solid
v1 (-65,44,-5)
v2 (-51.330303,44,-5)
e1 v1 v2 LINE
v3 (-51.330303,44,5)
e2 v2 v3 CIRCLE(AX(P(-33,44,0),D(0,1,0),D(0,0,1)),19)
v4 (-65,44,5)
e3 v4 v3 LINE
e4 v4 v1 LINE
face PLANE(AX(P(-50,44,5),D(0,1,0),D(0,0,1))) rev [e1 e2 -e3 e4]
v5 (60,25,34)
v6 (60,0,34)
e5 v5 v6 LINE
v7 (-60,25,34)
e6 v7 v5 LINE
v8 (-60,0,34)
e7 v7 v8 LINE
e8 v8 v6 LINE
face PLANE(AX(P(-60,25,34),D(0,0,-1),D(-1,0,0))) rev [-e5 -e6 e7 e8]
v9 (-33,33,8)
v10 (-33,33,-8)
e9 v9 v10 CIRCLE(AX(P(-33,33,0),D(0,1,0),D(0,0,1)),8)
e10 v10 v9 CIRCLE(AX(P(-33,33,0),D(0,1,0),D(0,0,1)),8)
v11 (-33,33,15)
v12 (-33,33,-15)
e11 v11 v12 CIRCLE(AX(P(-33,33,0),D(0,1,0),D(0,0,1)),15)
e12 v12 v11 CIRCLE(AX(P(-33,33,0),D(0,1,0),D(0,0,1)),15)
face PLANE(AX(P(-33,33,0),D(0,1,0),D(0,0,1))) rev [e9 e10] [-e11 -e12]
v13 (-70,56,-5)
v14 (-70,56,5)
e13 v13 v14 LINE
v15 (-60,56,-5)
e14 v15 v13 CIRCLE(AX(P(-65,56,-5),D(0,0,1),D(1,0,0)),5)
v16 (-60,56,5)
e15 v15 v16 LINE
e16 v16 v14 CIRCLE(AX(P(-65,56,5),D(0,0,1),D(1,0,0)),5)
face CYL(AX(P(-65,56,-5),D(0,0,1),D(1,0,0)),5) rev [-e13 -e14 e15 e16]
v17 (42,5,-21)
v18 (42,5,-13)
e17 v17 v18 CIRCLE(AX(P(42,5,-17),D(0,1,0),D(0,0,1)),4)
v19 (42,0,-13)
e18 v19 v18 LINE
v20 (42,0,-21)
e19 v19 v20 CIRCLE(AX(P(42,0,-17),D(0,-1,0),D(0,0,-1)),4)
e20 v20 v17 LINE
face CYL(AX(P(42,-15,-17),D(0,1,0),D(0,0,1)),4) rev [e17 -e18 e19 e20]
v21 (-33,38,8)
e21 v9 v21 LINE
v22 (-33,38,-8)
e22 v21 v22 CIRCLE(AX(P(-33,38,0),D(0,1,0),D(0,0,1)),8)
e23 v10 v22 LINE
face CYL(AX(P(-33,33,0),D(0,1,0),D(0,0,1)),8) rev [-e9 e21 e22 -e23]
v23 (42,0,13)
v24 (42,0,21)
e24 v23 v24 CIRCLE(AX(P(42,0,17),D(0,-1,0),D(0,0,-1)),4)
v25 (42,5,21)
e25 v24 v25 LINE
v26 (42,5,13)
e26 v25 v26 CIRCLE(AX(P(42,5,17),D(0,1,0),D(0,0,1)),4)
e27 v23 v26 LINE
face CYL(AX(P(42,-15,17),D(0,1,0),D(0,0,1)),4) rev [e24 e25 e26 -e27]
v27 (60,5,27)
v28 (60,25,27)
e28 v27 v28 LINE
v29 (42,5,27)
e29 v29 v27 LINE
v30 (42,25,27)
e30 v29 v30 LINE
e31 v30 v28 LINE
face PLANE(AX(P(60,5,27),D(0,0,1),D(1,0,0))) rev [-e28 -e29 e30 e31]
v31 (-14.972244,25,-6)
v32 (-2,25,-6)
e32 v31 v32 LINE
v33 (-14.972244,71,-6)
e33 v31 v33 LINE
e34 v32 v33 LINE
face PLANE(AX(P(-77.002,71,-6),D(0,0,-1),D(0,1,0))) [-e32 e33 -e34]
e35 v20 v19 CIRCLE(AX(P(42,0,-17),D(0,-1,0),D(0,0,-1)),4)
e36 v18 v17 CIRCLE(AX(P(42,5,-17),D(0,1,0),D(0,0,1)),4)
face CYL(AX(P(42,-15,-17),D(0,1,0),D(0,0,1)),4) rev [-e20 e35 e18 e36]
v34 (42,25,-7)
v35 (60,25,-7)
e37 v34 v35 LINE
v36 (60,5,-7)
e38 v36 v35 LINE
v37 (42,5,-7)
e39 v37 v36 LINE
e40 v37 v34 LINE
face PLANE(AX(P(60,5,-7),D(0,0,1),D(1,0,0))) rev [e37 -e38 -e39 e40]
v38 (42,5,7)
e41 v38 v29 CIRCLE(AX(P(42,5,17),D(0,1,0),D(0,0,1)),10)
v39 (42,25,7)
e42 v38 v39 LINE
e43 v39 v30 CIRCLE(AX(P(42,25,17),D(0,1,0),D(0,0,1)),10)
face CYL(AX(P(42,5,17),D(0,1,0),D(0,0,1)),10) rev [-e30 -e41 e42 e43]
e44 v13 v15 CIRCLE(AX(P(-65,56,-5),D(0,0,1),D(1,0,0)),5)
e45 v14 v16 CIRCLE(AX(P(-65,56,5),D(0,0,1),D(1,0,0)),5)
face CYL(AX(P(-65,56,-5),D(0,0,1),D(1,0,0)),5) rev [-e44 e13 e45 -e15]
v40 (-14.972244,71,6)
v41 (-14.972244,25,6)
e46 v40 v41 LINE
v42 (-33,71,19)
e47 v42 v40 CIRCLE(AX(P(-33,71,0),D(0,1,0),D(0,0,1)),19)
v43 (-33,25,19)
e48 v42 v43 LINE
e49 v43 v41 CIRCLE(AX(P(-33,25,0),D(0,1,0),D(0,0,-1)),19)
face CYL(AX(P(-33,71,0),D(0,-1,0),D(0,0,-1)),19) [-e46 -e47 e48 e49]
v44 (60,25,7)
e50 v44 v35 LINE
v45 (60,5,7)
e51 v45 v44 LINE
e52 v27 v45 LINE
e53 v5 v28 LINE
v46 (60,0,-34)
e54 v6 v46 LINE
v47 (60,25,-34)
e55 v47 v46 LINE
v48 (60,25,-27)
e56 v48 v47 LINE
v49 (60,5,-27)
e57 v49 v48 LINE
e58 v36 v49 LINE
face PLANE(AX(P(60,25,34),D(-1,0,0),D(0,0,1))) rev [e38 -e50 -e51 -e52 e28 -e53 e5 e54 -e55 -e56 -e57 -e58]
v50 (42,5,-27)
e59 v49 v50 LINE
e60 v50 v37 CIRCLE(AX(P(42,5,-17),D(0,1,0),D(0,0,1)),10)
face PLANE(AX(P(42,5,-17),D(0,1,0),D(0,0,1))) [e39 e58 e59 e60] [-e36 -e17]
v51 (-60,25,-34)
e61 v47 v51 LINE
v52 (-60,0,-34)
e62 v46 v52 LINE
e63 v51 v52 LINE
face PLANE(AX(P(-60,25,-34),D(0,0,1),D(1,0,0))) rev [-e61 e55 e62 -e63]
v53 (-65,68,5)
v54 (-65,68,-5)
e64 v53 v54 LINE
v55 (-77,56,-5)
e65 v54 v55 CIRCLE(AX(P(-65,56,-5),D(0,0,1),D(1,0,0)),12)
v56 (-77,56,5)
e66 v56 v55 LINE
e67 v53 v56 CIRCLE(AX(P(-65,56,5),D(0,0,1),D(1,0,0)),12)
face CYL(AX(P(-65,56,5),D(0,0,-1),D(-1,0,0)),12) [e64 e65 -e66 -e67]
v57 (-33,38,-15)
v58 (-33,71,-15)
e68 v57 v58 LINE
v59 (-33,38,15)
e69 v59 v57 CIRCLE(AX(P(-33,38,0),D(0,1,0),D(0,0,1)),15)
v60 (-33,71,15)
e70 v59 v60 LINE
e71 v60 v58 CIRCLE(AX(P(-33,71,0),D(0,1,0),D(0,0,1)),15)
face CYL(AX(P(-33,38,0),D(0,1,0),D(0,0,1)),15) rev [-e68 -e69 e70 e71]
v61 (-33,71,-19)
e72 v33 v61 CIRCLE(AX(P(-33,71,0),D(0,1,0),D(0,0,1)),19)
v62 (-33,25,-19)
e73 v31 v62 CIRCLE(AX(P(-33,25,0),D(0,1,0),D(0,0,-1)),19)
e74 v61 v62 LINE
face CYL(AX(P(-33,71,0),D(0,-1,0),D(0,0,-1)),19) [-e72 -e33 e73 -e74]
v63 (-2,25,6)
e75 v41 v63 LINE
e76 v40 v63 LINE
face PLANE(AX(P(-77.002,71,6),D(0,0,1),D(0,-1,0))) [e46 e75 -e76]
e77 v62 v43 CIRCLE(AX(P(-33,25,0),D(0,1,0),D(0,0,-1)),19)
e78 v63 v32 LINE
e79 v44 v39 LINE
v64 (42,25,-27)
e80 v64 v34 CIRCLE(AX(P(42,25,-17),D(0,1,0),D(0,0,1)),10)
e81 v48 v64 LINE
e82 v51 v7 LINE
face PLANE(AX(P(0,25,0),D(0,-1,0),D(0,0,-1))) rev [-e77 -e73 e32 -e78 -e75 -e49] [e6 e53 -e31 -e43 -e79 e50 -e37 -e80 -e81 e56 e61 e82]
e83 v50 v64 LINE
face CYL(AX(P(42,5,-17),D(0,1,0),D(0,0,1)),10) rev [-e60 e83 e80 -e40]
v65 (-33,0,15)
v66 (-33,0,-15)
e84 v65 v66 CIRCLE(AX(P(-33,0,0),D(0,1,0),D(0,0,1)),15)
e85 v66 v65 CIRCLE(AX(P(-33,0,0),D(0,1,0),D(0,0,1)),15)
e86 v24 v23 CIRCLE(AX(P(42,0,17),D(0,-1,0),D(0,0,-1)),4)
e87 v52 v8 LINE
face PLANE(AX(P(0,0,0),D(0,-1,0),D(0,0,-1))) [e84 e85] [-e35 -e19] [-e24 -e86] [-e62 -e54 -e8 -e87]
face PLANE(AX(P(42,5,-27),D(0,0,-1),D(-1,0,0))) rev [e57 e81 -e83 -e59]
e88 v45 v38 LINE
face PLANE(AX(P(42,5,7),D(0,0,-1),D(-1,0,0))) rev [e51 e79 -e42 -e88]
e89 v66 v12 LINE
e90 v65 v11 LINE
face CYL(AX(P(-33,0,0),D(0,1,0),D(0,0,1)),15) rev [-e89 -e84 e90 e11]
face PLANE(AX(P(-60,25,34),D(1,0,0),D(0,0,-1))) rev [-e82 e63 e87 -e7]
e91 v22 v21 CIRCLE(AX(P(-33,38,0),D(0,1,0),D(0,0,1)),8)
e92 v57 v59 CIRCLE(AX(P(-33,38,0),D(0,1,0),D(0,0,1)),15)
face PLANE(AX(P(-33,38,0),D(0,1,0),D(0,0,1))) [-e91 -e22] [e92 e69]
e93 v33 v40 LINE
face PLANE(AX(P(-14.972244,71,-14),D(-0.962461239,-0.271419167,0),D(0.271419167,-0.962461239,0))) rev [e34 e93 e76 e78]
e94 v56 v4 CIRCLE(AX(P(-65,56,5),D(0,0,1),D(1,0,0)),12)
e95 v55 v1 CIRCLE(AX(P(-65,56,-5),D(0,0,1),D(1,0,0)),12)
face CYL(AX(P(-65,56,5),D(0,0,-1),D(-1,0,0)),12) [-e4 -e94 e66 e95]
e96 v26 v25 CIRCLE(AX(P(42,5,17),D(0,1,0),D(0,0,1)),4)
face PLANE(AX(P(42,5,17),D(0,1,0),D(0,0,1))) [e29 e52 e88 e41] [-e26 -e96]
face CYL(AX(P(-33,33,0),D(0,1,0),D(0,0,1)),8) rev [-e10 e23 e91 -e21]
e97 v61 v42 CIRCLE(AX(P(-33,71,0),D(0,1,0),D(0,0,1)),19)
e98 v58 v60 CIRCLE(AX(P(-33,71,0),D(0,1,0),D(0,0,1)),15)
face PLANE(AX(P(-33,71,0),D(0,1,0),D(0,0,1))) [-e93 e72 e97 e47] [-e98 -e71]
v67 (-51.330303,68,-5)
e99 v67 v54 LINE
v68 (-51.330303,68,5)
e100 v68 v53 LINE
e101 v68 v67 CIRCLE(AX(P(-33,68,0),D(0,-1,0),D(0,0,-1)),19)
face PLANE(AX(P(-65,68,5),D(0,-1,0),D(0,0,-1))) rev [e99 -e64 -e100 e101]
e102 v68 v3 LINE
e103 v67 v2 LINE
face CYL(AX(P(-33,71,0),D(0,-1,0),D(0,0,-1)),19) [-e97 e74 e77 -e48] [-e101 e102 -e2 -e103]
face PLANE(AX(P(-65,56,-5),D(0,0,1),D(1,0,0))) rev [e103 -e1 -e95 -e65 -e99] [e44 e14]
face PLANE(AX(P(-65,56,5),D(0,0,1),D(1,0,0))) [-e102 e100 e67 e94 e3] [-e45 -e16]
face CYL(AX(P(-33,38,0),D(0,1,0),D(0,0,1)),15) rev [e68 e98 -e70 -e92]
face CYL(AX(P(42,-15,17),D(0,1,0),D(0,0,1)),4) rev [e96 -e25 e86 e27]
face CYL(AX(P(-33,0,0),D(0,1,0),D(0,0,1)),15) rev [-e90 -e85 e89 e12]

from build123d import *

# Parameters (mm, degrees)
BASE_PLATE_SKETCH_W   = 120
BASE_PLATE_SKETCH_H   = 68
BASE_PLATE_DEPTH      = 25
PIVOT_BOSS_SKETCH_R   = 19
PIVOT_BOSS_38_DEPTH   = 46
UPPER_BORE_SKETCH_R   = 15
UPPER_BORE_30_DEPTH   = 33
BORE_STEP_SKETCH_R    = 8
BORE_STEP_16_DEPTH    = 5
LOWER_BORE_SKETCH_R   = 15
LOWER_BORE_30_DEPTH   = 33
SIDE_LUG_DEPTH        = 5
LUG_HOLE_SKETCH_R     = 5
LUG_HOLE_10_DEPTH     = 10
U_SLOTS_2X20_DEPTH    = 20
SLOT_RELIEF_SKETCH_R  = 4
SLOT_RELIEF_CUT_DEPTH = 20
GUSSET_RIB_REACH      = 110.729
GUSSET_RIB_END_RADIUS = 19
GUSSET_RIB_SKETCH_W   = 12
GUSSET_RIB_SKETCH_H   = 46
RIB_TRIM_CUT_DEPTH    = 20


with BuildPart() as part:
    # Base Plate Sketch → Base Plate (new body)
    with BuildSketch(Plane(origin=(0, 0, 0), x_dir=(1, 0, 0), z_dir=(0, 1, 0))):
        Rectangle(BASE_PLATE_SKETCH_W, BASE_PLATE_SKETCH_H)
    extrude(amount=BASE_PLATE_DEPTH)

    # Pivot Boss Sketch → Pivot Boss Ø38 (add)
    with BuildSketch(Plane(origin=(0, 25, 0), x_dir=(1, 0, 0), z_dir=(0, 1, 0))):
        with Locations(Location((-33, 0, 0), (0, 0, 90))):
            Circle(PIVOT_BOSS_SKETCH_R)
    extrude(amount=PIVOT_BOSS_38_DEPTH)

    # Upper Bore Sketch → Upper Bore Ø30 (cut)
    with BuildSketch(Plane(origin=(0, 71, 0), x_dir=(1, 0, 0), z_dir=(0, 1, 0))):
        with Locations(Location((-33, 0, 0), (0, 0, 270))):
            Circle(UPPER_BORE_SKETCH_R)
    extrude(amount=-UPPER_BORE_30_DEPTH, mode=Mode.SUBTRACT)

    # Bore Step Sketch → Bore Step Ø16 (cut)
    with BuildSketch(Plane(origin=(0, 38, 0), x_dir=(1, 0, 0), z_dir=(0, 1, 0))):
        with Locations(Location((-33, 0, 0), (0, 0, 270))):
            Circle(BORE_STEP_SKETCH_R)
    extrude(amount=-BORE_STEP_16_DEPTH, mode=Mode.SUBTRACT)

    # Lower Bore Sketch → Lower Bore Ø30 (cut)
    with BuildSketch(Plane(origin=(0, 33, 0), x_dir=(1, 0, 0), z_dir=(0, 1, 0))):
        with Locations(Location((-33, 0, 0), (0, 0, 270))):
            Circle(LOWER_BORE_SKETCH_R)
    extrude(amount=-LOWER_BORE_30_DEPTH, mode=Mode.SUBTRACT)

    # Side Lug Sketch → Side Lug (add, symmetric)
    with BuildSketch(Plane.XY):
        with BuildLine():
            Line((-65, 68), (-50, 68))
            Line((-50, 68), (-50, 44))
            Line((-50, 44), (-65, 44))
            ThreePointArc((-65, 44), (-77, 56), (-65, 68))
        make_face()
    extrude(amount=SIDE_LUG_DEPTH, both=True)

    # Lug Hole Sketch → Lug Hole Ø10 (cut)
    with BuildSketch(Plane.XY.offset(5)):
        with Locations((-65, 56)):
            Circle(LUG_HOLE_SKETCH_R)
    extrude(amount=-LUG_HOLE_10_DEPTH, mode=Mode.SUBTRACT)

    # U-Slots Sketch → U-Slots 2x20 (cut)
    with BuildSketch(Plane(origin=(0, 25, 0), x_dir=(1, 0, 0), z_dir=(0, 1, 0))):
        with BuildLine():
            Line((42, 27), (60, 27))
            Line((60, 27), (60, 7))
            Line((60, 7), (42, 7))
            ThreePointArc((42, 7), (32, 17), (42, 27))
        make_face()
        with BuildLine():
            Line((42, -7), (60, -7))
            Line((60, -7), (60, -27))
            Line((60, -27), (42, -27))
            ThreePointArc((42, -27), (32, -17), (42, -7))
        make_face()
    extrude(amount=-U_SLOTS_2X20_DEPTH, mode=Mode.SUBTRACT)

    # Slot Relief Sketch → Slot Relief Cut (cut)
    with BuildSketch(Plane(origin=(0, 5, 0), x_dir=(1, 0, 0), z_dir=(0, 1, 0))):
        with Locations(Location((42, 17, 0), (0, 0, 270))):
            Circle(SLOT_RELIEF_SKETCH_R)
        with Locations(Location((42, -17, 0), (0, 0, 270))):
            Circle(SLOT_RELIEF_SKETCH_R)
    extrude(amount=-SLOT_RELIEF_CUT_DEPTH, mode=Mode.SUBTRACT)

    # Gusset Rib: up to this cylinder (the profile starts outside it)
    gusset_rib_end = Plane(origin=(-33, 48, 0), z_dir=(0, -1, 0)) * Cylinder(GUSSET_RIB_END_RADIUS, 260.458, mode=Mode.PRIVATE)
    # Gusset Rib Sketch → Gusset Rib (add, up to the surface)
    with BuildSketch(Plane(origin=(-2, 0, 0), x_dir=(0, 0, -1), z_dir=(1, 0, 0)), mode=Mode.PRIVATE) as gusset_rib_sk1:
        with Locations((0, 48)):
            Rectangle(GUSSET_RIB_SKETCH_W, GUSSET_RIB_SKETCH_H)
    gusset_rib_tool1 = extrude(gusset_rib_sk1.sketch, amount=-GUSSET_RIB_REACH, mode=Mode.PRIVATE) - gusset_rib_end
    add(gusset_rib_tool1.solids().sort_by_distance((-2, 48, 0))[0])

    # Rib Trim Sketch → Rib Trim Cut (cut)
    with BuildSketch(Plane.XY.offset(6)):
        Polygon((-14.972243623, 71), (-2, 25), (-2, 71), align=None)
    extrude(amount=-RIB_TRIM_CUT_DEPTH, mode=Mode.SUBTRACT)


solid = part.part
